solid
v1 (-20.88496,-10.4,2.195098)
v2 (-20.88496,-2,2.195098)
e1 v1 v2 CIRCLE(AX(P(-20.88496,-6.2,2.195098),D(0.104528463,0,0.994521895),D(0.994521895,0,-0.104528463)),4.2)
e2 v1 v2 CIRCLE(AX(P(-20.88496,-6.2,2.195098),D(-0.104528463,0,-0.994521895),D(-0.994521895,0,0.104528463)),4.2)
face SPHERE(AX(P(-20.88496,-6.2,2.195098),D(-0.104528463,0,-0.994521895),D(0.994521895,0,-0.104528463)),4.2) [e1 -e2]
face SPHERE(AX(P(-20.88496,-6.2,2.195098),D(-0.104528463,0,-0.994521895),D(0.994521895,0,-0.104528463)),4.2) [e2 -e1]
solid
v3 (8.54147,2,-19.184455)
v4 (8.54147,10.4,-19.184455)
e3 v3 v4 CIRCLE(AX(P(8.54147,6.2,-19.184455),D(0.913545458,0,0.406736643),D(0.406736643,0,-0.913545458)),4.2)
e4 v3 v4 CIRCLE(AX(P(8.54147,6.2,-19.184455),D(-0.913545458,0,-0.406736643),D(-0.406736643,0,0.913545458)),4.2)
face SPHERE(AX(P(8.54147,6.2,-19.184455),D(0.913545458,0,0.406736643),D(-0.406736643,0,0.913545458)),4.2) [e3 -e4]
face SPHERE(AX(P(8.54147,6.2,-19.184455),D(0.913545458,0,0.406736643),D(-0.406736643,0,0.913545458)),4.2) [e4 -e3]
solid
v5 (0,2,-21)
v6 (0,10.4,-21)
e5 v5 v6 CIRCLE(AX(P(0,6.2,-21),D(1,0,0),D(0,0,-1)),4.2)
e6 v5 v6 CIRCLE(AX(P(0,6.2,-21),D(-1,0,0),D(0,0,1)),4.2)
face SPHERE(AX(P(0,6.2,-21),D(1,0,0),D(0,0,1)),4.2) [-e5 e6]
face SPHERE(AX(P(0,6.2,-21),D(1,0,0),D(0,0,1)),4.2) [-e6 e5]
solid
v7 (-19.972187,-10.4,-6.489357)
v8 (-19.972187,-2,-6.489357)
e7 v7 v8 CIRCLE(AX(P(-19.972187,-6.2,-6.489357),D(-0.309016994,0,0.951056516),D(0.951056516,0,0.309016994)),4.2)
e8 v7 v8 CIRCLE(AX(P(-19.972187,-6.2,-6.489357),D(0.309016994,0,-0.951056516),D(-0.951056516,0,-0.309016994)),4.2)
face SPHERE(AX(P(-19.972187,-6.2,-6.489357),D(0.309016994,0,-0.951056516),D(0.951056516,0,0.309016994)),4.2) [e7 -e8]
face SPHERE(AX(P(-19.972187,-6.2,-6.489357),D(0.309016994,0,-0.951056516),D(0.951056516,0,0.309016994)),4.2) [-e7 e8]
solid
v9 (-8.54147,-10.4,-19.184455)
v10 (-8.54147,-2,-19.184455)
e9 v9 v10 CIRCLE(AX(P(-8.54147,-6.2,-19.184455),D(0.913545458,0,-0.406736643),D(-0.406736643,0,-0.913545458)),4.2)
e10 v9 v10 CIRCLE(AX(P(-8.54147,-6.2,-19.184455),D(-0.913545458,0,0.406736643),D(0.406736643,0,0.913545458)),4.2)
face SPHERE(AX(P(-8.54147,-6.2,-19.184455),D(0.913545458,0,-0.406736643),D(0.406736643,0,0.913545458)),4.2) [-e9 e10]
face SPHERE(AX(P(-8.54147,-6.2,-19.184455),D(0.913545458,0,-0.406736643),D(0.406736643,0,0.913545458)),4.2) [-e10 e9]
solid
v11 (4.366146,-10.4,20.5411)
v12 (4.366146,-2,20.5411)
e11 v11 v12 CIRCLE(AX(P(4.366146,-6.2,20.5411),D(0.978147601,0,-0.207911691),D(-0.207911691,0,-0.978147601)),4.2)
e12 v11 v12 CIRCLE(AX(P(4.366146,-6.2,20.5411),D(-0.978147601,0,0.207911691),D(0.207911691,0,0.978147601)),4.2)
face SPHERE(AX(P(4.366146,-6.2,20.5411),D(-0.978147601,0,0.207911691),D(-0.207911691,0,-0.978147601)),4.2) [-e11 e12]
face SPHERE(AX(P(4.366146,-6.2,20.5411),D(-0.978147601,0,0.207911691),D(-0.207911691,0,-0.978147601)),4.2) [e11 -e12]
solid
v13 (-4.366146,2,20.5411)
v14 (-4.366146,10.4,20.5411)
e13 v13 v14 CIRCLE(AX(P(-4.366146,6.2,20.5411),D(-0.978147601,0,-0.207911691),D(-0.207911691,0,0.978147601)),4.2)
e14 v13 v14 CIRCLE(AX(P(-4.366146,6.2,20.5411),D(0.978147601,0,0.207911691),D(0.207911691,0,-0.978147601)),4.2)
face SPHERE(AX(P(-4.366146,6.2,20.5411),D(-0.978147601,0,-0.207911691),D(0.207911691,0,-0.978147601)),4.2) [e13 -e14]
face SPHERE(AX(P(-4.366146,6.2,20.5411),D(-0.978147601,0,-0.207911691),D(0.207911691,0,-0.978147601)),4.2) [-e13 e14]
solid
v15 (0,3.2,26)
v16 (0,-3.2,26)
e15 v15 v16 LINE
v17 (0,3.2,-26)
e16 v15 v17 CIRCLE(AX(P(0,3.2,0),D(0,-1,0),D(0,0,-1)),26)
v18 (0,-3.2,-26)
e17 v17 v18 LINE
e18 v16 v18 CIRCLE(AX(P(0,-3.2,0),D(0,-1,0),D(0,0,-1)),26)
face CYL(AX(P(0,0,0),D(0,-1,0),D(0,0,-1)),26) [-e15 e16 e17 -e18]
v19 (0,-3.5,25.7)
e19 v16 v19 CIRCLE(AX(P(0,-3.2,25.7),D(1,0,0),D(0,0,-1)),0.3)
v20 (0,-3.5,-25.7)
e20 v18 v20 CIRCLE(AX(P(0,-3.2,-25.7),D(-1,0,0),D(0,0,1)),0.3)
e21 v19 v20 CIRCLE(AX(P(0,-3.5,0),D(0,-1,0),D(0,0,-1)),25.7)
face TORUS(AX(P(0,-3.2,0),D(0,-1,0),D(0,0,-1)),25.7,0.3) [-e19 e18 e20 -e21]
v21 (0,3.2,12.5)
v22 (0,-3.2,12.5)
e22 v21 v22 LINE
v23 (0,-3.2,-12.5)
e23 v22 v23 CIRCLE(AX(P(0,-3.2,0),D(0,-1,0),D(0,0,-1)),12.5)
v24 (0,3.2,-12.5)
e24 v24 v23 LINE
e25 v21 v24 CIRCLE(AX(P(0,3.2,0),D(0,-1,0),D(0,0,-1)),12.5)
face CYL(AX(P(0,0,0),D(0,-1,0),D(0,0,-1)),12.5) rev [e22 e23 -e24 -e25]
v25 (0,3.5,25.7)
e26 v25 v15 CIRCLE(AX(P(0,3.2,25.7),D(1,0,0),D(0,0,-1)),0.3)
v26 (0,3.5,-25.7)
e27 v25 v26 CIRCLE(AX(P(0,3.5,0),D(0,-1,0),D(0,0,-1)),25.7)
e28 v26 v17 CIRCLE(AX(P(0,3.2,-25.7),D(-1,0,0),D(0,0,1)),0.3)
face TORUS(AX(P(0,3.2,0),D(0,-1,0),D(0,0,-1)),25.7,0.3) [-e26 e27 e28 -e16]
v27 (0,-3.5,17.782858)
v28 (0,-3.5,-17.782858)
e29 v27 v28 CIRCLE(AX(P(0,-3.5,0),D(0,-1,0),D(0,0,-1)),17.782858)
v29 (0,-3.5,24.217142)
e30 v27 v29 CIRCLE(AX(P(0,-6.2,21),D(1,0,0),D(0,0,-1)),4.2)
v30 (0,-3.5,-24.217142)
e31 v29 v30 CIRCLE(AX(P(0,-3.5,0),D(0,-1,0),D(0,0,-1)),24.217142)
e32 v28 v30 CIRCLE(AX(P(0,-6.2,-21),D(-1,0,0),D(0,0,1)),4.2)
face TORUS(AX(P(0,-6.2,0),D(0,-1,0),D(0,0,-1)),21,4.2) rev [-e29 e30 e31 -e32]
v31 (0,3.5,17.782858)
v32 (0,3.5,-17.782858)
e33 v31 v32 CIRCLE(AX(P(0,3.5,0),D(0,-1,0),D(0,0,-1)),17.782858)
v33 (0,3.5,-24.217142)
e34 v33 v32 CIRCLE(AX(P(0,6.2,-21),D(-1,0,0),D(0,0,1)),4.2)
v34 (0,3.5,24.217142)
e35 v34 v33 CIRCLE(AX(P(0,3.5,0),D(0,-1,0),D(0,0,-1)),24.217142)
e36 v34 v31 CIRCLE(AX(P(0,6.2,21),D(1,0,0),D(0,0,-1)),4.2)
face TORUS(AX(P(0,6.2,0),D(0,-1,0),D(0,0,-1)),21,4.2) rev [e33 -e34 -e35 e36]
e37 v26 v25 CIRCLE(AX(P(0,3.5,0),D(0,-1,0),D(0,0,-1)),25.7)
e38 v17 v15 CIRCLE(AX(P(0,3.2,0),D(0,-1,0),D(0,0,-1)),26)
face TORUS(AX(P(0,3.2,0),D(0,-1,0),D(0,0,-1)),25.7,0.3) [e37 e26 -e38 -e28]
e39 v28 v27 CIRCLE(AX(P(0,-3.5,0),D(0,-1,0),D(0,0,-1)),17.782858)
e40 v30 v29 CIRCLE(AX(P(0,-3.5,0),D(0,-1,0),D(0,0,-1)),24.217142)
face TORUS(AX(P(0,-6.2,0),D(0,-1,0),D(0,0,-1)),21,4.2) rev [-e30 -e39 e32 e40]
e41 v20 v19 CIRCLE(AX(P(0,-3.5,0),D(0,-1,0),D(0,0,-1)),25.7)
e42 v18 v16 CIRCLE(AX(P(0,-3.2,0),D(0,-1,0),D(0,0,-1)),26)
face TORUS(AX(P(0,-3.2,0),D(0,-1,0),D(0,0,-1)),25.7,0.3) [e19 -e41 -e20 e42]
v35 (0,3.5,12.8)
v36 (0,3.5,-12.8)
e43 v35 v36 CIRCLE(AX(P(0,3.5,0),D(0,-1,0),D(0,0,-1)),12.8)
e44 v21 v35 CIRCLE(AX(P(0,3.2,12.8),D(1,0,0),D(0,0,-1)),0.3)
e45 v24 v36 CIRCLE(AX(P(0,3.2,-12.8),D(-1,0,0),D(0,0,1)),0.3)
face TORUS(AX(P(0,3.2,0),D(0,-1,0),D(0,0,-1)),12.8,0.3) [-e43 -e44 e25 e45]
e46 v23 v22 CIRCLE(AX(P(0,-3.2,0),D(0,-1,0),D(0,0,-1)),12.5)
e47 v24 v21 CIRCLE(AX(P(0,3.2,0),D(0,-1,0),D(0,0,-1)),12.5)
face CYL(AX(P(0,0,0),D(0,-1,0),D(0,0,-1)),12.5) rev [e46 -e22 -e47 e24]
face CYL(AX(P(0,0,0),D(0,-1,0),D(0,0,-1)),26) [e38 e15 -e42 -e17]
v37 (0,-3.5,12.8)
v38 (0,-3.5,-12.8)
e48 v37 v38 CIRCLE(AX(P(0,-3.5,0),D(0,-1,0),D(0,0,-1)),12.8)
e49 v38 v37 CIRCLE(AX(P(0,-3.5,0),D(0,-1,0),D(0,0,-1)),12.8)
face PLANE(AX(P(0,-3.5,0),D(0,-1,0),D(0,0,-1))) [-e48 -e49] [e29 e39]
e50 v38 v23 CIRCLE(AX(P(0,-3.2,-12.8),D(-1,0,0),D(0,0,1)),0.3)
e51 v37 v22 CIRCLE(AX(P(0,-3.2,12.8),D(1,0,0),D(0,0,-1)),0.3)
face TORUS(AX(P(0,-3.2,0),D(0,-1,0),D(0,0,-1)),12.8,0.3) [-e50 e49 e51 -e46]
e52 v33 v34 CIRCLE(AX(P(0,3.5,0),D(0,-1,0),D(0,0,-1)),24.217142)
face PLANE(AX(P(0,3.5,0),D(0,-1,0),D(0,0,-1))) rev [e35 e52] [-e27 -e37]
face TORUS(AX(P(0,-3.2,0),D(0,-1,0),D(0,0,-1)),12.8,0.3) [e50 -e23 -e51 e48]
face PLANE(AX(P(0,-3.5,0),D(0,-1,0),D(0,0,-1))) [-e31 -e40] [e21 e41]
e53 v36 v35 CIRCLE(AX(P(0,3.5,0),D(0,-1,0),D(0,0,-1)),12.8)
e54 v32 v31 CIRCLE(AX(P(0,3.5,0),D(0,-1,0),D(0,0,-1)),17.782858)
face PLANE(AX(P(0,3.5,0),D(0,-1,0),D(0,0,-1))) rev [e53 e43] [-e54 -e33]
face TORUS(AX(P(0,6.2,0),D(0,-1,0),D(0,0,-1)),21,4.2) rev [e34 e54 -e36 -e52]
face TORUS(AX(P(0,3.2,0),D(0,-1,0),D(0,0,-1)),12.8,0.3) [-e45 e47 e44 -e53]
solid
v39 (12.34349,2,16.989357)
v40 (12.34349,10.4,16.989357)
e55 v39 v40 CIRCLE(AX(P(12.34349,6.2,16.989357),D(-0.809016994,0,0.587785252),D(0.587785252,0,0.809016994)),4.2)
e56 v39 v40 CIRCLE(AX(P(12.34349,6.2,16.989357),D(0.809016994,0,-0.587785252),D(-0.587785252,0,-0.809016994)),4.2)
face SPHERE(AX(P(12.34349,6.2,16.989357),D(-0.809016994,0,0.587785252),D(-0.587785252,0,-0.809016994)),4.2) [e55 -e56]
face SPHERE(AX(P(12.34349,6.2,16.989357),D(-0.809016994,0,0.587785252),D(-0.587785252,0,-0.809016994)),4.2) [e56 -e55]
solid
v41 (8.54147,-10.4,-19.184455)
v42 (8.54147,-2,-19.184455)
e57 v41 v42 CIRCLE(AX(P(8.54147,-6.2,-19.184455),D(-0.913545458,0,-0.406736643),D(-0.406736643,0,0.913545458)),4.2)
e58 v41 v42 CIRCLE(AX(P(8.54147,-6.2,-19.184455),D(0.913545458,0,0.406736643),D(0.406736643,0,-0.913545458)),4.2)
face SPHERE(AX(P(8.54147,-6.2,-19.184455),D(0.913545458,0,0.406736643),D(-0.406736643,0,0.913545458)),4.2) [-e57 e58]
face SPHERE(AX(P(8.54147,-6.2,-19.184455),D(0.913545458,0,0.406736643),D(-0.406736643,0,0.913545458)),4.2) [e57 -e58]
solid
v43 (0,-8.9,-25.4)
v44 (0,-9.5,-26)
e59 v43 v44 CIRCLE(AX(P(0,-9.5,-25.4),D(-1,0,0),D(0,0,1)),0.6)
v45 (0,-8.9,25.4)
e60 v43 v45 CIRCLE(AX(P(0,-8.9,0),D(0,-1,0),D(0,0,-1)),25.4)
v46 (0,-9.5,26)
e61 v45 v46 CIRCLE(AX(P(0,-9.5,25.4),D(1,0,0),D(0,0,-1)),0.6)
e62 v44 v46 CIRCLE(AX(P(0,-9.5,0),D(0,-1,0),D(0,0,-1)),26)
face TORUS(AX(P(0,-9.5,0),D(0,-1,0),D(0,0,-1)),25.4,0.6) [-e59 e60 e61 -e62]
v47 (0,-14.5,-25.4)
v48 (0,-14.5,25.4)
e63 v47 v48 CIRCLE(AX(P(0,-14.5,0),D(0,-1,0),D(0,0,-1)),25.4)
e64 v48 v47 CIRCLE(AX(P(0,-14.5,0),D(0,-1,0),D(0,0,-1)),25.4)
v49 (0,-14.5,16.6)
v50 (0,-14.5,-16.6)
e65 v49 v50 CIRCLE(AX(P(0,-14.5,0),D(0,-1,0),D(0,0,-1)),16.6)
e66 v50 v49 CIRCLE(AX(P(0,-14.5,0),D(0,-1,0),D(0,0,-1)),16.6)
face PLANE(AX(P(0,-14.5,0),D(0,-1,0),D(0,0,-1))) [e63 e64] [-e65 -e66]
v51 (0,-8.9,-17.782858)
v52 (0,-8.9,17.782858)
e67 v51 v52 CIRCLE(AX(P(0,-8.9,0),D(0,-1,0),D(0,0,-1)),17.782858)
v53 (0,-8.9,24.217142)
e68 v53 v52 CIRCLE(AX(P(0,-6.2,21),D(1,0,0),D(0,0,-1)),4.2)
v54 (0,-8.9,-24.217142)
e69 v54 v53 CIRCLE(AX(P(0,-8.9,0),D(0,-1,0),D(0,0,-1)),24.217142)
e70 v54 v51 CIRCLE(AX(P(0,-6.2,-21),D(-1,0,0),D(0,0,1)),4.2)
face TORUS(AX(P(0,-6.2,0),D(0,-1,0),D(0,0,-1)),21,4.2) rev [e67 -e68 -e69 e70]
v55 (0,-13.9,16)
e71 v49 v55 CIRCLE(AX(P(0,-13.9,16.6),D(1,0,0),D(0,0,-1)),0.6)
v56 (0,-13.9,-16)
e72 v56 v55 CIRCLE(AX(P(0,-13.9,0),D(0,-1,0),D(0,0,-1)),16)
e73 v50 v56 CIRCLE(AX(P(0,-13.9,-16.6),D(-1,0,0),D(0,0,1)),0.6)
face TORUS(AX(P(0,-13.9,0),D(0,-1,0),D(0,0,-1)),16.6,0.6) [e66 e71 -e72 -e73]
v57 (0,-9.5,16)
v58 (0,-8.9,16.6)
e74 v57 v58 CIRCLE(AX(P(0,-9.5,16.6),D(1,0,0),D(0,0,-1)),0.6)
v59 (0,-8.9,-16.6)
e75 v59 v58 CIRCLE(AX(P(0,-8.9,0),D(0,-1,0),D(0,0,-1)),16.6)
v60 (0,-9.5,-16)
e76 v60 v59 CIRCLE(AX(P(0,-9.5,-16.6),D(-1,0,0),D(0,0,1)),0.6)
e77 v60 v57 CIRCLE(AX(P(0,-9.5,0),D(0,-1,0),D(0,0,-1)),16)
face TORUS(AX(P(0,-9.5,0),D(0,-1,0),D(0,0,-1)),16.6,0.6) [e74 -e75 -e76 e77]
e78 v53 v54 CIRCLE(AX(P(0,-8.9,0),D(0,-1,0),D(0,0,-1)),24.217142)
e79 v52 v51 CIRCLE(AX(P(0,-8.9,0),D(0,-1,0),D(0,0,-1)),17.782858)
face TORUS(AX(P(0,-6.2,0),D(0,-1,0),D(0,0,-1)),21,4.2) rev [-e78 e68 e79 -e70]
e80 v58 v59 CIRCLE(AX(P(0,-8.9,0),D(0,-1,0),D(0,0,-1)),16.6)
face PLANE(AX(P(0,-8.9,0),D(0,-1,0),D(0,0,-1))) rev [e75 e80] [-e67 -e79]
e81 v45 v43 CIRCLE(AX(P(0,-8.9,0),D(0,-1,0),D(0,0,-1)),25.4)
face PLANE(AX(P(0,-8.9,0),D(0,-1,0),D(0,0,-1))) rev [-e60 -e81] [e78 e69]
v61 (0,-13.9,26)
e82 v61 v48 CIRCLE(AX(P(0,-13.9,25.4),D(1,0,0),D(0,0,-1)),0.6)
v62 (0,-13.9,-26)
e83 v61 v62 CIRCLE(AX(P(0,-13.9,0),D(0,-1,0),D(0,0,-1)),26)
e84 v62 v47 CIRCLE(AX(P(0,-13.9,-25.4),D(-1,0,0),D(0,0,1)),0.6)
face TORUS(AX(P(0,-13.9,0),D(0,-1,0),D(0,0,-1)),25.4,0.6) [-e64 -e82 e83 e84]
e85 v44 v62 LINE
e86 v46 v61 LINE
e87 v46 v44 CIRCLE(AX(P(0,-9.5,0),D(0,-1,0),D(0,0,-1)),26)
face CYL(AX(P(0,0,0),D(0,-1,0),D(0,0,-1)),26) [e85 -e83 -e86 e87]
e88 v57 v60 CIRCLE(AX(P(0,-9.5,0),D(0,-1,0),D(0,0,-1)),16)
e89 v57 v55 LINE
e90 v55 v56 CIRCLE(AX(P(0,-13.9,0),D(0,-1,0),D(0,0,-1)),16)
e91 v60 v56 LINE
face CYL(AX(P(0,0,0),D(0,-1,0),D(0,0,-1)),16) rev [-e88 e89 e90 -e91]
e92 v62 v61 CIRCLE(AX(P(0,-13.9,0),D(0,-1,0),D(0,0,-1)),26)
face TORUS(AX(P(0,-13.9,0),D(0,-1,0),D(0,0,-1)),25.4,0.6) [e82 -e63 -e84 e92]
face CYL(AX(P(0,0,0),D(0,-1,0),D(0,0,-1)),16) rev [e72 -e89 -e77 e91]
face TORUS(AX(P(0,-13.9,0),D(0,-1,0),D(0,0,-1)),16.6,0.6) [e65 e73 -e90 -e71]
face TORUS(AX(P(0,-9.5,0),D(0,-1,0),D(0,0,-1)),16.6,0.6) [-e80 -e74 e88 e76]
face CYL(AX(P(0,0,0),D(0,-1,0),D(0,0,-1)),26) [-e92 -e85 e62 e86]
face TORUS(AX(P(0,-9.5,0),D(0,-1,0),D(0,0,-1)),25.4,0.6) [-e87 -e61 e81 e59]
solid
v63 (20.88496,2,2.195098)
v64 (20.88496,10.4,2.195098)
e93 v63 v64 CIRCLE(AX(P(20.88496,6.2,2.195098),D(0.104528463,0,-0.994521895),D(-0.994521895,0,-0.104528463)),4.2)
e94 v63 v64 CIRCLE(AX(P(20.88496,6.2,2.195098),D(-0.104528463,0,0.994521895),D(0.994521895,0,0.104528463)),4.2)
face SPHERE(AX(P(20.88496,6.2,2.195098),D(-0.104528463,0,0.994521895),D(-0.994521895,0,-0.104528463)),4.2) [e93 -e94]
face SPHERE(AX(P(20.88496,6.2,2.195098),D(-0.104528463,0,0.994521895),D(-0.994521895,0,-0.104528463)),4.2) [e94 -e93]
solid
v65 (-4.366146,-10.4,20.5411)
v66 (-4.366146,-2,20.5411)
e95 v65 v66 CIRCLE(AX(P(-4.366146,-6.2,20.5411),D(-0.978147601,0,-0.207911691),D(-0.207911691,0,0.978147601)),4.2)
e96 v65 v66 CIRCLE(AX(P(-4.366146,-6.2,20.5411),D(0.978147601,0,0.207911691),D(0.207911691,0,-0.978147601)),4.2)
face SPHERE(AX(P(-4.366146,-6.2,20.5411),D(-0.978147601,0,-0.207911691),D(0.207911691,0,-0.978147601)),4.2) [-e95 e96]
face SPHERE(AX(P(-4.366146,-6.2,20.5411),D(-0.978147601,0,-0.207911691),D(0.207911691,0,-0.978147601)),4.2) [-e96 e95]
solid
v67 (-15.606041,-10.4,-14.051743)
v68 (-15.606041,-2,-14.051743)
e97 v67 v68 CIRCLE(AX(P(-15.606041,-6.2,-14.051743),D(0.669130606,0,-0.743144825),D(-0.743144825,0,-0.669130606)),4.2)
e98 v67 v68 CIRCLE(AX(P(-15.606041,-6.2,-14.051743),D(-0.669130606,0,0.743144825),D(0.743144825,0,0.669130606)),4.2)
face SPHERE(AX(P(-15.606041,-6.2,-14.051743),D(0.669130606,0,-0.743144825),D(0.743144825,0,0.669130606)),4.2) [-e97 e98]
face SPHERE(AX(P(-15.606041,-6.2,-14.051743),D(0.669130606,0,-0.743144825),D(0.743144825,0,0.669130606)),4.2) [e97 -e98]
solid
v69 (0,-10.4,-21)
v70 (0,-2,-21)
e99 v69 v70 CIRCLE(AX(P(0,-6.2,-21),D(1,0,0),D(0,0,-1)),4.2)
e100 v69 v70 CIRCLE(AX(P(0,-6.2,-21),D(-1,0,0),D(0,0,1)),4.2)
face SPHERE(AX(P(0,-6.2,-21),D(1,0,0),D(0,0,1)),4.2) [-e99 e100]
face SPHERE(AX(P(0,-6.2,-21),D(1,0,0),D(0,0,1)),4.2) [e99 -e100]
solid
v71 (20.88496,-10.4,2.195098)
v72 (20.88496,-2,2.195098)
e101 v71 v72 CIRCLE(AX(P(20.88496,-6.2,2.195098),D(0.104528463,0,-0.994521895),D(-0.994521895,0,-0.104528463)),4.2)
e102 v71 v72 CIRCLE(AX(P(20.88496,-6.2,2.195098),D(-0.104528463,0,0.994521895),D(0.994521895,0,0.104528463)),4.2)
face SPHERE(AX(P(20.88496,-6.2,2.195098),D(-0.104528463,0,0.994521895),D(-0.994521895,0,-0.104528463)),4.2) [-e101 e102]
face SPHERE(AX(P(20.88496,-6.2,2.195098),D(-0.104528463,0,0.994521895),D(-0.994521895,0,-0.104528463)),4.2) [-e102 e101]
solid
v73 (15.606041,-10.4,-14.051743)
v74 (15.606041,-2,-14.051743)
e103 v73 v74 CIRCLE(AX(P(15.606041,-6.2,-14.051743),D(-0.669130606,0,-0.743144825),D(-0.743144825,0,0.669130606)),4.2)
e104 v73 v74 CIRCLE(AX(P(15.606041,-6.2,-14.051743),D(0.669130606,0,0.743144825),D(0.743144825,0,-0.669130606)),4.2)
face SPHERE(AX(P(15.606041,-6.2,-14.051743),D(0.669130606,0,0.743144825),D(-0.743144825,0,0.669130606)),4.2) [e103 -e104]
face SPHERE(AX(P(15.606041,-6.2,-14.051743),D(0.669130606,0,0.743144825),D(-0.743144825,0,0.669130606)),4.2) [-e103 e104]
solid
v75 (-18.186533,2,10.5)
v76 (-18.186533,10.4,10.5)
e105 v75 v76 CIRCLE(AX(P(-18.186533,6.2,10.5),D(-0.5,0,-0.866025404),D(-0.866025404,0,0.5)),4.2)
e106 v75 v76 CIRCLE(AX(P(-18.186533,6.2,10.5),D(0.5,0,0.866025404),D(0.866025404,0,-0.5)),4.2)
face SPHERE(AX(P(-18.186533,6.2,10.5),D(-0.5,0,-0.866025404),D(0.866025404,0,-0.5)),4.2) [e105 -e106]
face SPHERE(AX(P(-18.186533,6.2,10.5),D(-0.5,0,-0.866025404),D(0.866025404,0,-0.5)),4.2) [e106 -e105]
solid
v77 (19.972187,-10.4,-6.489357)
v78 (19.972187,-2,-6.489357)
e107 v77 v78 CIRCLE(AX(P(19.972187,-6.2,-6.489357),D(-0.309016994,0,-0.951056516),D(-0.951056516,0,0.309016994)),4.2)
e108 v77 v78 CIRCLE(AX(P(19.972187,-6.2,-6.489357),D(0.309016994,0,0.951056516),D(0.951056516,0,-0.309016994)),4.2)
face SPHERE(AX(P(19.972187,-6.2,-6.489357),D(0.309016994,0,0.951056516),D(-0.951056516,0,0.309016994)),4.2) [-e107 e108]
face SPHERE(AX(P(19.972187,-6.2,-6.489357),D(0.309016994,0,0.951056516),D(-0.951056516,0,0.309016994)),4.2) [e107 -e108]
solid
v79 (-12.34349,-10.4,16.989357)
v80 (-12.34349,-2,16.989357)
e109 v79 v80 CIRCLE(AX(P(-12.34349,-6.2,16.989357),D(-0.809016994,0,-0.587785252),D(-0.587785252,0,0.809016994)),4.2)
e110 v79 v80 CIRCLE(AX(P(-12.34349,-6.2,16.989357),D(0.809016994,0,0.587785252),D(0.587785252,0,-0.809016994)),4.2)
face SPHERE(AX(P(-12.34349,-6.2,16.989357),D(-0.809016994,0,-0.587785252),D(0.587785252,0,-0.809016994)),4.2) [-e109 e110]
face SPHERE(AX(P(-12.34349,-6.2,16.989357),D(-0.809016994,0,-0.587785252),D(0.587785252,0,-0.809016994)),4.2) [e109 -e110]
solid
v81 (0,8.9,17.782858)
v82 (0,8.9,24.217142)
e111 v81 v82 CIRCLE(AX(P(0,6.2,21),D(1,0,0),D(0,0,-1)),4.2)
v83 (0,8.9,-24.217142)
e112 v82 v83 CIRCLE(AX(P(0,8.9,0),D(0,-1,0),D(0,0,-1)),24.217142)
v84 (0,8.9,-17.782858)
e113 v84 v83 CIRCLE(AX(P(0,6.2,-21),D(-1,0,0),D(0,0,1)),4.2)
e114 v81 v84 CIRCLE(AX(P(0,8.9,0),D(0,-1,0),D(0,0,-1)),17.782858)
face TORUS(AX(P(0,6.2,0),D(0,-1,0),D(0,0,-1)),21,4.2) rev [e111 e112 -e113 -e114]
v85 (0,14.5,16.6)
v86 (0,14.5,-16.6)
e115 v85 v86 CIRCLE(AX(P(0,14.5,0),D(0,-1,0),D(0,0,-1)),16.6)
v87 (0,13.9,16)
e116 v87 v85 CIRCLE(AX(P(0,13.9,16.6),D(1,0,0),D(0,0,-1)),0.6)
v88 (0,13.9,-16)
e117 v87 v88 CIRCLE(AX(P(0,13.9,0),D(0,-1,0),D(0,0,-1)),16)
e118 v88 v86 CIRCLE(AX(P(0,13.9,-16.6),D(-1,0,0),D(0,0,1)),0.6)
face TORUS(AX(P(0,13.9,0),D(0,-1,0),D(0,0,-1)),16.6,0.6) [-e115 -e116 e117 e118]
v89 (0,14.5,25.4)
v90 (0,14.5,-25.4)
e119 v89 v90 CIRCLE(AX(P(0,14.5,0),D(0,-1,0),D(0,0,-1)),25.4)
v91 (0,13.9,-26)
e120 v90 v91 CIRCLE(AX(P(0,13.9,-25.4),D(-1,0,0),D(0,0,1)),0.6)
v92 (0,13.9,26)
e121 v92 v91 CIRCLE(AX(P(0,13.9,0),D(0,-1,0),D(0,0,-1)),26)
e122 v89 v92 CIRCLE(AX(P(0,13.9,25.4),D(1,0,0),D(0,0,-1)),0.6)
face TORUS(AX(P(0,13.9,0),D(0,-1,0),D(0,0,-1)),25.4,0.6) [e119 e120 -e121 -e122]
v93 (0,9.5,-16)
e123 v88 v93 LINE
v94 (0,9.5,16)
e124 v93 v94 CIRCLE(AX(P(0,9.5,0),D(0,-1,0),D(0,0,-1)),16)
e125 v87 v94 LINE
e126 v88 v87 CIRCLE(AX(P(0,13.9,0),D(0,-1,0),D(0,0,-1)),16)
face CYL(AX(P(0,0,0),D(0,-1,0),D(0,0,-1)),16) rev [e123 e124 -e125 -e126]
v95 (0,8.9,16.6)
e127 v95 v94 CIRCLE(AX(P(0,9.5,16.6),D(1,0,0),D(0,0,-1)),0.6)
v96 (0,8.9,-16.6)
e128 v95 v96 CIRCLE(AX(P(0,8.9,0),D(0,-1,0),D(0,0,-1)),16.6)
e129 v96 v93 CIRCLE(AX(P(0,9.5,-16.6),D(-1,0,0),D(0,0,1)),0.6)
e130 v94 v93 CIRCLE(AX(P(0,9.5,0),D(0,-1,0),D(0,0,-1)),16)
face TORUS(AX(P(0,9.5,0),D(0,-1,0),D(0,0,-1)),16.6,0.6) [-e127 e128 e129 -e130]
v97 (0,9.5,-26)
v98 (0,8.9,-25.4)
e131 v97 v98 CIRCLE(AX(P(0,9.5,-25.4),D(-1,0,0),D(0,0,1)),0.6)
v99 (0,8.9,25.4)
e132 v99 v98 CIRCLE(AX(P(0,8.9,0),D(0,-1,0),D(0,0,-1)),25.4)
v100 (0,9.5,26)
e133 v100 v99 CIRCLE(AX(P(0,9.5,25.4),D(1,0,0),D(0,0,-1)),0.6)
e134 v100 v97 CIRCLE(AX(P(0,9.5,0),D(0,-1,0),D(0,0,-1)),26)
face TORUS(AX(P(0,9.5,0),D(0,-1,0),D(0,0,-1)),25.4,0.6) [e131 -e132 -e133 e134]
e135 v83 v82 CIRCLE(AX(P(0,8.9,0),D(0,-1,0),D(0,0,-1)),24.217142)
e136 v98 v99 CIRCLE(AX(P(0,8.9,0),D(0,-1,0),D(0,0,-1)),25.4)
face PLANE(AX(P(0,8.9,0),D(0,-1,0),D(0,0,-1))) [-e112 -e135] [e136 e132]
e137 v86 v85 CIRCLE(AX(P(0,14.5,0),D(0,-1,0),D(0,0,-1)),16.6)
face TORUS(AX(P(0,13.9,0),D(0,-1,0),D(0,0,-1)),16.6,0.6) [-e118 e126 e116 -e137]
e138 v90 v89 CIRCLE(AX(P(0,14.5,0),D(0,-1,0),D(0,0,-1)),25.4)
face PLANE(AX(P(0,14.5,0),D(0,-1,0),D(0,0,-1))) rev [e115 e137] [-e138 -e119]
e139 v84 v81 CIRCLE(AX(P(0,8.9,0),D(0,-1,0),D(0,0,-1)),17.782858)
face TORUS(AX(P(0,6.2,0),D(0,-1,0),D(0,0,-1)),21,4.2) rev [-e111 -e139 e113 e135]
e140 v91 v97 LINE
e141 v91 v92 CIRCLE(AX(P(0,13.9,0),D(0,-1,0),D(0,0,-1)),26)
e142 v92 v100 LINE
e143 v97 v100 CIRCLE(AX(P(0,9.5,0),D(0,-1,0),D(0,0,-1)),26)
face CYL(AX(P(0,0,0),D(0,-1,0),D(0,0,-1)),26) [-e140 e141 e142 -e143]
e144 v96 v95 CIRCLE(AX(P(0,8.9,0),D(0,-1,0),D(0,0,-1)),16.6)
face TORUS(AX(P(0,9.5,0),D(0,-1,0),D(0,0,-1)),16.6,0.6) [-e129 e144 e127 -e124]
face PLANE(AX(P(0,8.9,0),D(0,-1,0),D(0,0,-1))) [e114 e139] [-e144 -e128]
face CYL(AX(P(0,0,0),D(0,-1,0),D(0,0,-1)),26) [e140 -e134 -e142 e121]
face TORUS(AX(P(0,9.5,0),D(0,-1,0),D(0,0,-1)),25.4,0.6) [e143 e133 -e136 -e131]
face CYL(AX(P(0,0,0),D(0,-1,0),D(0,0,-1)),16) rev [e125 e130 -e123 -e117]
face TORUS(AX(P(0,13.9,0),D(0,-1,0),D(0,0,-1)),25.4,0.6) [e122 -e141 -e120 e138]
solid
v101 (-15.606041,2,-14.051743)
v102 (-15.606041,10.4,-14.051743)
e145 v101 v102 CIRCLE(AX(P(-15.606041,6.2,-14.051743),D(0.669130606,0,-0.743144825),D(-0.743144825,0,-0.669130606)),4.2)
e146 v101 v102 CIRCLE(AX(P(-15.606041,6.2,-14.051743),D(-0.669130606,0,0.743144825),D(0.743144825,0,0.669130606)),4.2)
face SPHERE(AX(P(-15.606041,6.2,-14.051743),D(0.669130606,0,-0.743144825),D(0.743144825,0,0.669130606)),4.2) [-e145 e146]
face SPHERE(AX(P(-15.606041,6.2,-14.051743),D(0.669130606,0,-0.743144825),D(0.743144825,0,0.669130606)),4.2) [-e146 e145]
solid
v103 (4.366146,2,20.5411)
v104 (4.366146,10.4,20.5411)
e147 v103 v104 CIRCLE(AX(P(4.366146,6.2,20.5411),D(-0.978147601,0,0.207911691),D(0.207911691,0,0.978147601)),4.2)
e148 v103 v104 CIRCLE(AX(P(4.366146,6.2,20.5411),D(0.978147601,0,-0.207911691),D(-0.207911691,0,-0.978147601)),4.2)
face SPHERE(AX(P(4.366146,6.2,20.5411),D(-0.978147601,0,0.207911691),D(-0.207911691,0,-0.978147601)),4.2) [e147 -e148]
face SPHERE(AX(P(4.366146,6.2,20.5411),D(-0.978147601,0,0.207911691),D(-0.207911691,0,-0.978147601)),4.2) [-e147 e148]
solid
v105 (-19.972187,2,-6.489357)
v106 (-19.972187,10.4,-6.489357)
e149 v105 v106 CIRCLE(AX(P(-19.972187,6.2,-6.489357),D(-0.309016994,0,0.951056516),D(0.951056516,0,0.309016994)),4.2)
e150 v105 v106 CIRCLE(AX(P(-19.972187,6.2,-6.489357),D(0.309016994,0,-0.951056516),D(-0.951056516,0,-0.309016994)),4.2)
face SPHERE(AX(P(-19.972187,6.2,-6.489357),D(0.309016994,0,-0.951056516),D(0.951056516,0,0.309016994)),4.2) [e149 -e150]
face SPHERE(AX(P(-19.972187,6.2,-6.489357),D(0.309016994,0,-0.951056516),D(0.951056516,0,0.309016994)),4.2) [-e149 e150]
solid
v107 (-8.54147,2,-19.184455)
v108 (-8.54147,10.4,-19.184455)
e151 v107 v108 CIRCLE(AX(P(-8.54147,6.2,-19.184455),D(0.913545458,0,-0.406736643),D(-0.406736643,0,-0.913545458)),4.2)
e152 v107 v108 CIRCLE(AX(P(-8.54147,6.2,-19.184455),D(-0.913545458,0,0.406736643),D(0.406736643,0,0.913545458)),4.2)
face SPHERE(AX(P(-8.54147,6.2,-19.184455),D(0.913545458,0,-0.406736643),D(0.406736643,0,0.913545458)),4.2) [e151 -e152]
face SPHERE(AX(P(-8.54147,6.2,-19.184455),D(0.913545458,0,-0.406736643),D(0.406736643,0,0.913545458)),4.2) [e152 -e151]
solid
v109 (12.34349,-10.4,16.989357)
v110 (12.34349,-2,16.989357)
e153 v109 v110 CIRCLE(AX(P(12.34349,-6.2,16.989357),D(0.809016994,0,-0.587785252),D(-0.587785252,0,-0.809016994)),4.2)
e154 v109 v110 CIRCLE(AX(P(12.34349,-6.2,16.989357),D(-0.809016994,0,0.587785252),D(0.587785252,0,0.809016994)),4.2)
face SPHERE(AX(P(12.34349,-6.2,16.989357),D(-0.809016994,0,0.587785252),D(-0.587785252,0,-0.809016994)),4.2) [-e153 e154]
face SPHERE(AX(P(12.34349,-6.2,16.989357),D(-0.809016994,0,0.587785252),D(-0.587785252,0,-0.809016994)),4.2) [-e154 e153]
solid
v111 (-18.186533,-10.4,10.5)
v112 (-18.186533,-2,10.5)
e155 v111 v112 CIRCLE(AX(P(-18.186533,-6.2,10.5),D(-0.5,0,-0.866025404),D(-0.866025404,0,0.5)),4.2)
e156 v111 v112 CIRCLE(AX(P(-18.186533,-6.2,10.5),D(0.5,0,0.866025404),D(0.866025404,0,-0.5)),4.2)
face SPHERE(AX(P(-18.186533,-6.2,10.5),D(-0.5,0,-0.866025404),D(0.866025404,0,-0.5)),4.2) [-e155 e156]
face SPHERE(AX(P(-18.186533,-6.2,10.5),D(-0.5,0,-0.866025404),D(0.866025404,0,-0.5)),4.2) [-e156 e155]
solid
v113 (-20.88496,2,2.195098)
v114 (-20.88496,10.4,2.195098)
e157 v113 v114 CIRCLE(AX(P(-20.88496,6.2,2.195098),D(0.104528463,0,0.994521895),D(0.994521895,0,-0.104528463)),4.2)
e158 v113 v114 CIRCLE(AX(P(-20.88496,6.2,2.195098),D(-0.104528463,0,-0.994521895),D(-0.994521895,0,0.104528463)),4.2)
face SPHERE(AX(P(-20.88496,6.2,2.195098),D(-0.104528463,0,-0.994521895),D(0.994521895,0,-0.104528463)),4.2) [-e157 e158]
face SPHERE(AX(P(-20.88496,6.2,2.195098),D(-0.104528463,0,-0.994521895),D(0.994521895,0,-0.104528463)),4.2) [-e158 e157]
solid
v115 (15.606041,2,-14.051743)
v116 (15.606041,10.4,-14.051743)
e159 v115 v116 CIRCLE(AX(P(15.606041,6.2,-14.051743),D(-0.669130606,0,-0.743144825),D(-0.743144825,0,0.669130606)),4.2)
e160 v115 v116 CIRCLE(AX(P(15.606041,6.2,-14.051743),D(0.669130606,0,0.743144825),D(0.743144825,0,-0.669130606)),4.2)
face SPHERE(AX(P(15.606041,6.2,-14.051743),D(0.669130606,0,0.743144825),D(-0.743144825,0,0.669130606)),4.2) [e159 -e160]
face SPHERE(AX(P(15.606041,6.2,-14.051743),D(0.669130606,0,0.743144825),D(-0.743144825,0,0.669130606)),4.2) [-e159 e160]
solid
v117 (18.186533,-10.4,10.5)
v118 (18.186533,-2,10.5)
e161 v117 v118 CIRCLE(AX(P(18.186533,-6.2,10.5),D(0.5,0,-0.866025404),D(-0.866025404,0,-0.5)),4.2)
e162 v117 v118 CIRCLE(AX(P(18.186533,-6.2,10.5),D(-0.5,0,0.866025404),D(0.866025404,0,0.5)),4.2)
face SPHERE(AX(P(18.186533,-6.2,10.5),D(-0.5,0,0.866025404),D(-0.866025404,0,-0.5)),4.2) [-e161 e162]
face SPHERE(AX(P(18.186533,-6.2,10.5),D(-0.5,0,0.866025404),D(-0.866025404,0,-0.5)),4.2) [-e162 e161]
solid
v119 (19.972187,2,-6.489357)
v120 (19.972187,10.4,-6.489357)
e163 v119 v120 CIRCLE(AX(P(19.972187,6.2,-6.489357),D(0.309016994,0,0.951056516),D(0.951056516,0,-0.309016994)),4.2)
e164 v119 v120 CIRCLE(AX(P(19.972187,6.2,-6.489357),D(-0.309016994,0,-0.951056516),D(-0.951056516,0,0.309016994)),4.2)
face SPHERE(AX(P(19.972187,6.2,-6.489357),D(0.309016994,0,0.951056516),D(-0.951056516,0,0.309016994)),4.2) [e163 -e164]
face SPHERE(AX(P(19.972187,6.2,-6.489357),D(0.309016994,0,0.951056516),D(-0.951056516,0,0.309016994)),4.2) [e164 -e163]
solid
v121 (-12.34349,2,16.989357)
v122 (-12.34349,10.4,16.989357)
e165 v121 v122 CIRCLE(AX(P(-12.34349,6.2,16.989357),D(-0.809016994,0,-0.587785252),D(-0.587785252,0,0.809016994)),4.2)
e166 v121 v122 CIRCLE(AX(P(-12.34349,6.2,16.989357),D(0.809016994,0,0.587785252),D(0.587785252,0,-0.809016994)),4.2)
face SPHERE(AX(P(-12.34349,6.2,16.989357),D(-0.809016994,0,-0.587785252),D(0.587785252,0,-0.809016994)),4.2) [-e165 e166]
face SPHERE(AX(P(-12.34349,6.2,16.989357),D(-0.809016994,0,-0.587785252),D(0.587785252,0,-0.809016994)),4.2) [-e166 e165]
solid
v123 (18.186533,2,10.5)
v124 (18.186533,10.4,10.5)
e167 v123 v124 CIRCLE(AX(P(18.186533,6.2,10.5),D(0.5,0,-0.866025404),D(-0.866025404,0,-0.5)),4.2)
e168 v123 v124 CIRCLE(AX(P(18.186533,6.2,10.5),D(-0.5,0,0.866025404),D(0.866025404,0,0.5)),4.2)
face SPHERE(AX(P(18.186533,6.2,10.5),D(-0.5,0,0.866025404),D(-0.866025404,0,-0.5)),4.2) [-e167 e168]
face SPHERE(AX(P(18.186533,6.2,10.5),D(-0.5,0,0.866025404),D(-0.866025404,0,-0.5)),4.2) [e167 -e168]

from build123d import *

# Parameters (mm, degrees)
CIRPATTERN5_COUNT = 15


with BuildPart() as part:
    # Sketch2 → Revolve1 (revolve)
    with BuildSketch(Plane(origin=(0, 0, 0), x_dir=(0, 0, -1), z_dir=(1, 0, 0))):
        with BuildLine():
            ThreePointArc((24.217141588, 8.9), (21, 10.4), (17.782858412, 8.9))
            Line((17.782858412, 8.9), (16.6, 8.9))
            ThreePointArc((16.6, 8.9), (16.175735931, 9.075735931), (16, 9.5))
            Line((16, 9.5), (16, 13.9))
            ThreePointArc((16, 13.9), (16.175735931, 14.324264069), (16.6, 14.5))
            Line((16.6, 14.5), (25.4, 14.5))
            ThreePointArc((25.4, 14.5), (25.824264069, 14.324264069), (26, 13.9))
            Line((26, 13.9), (26, 9.5))
            ThreePointArc((26, 9.5), (25.824264069, 9.075735931), (25.4, 8.9))
            Line((25.4, 8.9), (24.217141588, 8.9))
        make_face()
        with BuildLine():
            ThreePointArc((17.782858412, 3.5), (21, 2), (24.217141588, 3.5))
            Line((24.217141588, 3.5), (25.7, 3.5))
            ThreePointArc((25.7, 3.5), (25.912132034, 3.412132034), (26, 3.2))
            Line((26, 3.2), (26, -3.2))
            ThreePointArc((26, -3.2), (25.912132034, -3.412132034), (25.7, -3.5))
            Line((25.7, -3.5), (24.217141588, -3.5))
            ThreePointArc((24.217141588, -3.5), (21, -2), (17.782858412, -3.5))
            Line((17.782858412, -3.5), (12.8, -3.5))
            ThreePointArc((12.8, -3.5), (12.587867966, -3.412132034), (12.5, -3.2))
            Line((12.5, -3.2), (12.5, 3.2))
            ThreePointArc((12.5, 3.2), (12.587867966, 3.412132034), (12.8, 3.5))
            Line((12.8, 3.5), (17.782858412, 3.5))
        make_face()
        with BuildLine():
            ThreePointArc((17.782858412, -8.9), (21, -10.4), (24.217141588, -8.9))
            Line((24.217141588, -8.9), (25.4, -8.9))
            ThreePointArc((25.4, -8.9), (25.824264069, -9.075735931), (26, -9.5))
            Line((26, -9.5), (26, -13.9))
            ThreePointArc((26, -13.9), (25.824264069, -14.324264069), (25.4, -14.5))
            Line((25.4, -14.5), (16.6, -14.5))
            ThreePointArc((16.6, -14.5), (16.175735931, -14.324264069), (16, -13.9))
            Line((16, -13.9), (16, -9.5))
            ThreePointArc((16, -9.5), (16.175735931, -9.075735931), (16.6, -8.9))
            Line((16.6, -8.9), (17.782858412, -8.9))
        make_face()
    revolve(axis=Axis((0, 0, 0), (0, 1, 0)))


with BuildPart() as body_2:
    # Sketch3 → Revolve2 (revolve)
    with BuildSketch(Plane(origin=(0, 0, 0), x_dir=(0, 0, -1), z_dir=(1, 0, 0))):
        with BuildLine():
            ThreePointArc((21, 2), (25.2, 6.2), (21, 10.4))
            Line((21, 10.4), (21, 2))
        make_face()
        with BuildLine():
            ThreePointArc((21, -10.4), (25.2, -6.2), (21, -2))
            Line((21, -2), (21, -10.4))
        make_face()
    revolve(axis=Axis((0, 10.4, -21), (0, -1, 0)))


with BuildPart() as cirpattern5_1:
    # CirPattern5: pattern copy
    add(body_2.part.rotate(Axis((0, 0, 0), (0, 1, 0)), 1 * 360 / CIRPATTERN5_COUNT))


with BuildPart() as cirpattern5_2:
    # CirPattern5: pattern copy
    add(body_2.part.rotate(Axis((0, 0, 0), (0, 1, 0)), 2 * 360 / CIRPATTERN5_COUNT))


with BuildPart() as cirpattern5_3:
    # CirPattern5: pattern copy
    add(body_2.part.rotate(Axis((0, 0, 0), (0, 1, 0)), 3 * 360 / CIRPATTERN5_COUNT))


with BuildPart() as cirpattern5_4:
    # CirPattern5: pattern copy
    add(body_2.part.rotate(Axis((0, 0, 0), (0, 1, 0)), 4 * 360 / CIRPATTERN5_COUNT))


with BuildPart() as cirpattern5_5:
    # CirPattern5: pattern copy
    add(body_2.part.rotate(Axis((0, 0, 0), (0, 1, 0)), 5 * 360 / CIRPATTERN5_COUNT))


with BuildPart() as cirpattern5_6:
    # CirPattern5: pattern copy
    add(body_2.part.rotate(Axis((0, 0, 0), (0, 1, 0)), 6 * 360 / CIRPATTERN5_COUNT))


with BuildPart() as cirpattern5_7:
    # CirPattern5: pattern copy
    add(body_2.part.rotate(Axis((0, 0, 0), (0, 1, 0)), 7 * 360 / CIRPATTERN5_COUNT))


with BuildPart() as cirpattern5_8:
    # CirPattern5: pattern copy
    add(body_2.part.rotate(Axis((0, 0, 0), (0, 1, 0)), 8 * 360 / CIRPATTERN5_COUNT))


with BuildPart() as cirpattern5_9:
    # CirPattern5: pattern copy
    add(body_2.part.rotate(Axis((0, 0, 0), (0, 1, 0)), 9 * 360 / CIRPATTERN5_COUNT))


with BuildPart() as cirpattern5_10:
    # CirPattern5: pattern copy
    add(body_2.part.rotate(Axis((0, 0, 0), (0, 1, 0)), 10 * 360 / CIRPATTERN5_COUNT))


with BuildPart() as cirpattern5_11:
    # CirPattern5: pattern copy
    add(body_2.part.rotate(Axis((0, 0, 0), (0, 1, 0)), 11 * 360 / CIRPATTERN5_COUNT))


with BuildPart() as cirpattern5_12:
    # CirPattern5: pattern copy
    add(body_2.part.rotate(Axis((0, 0, 0), (0, 1, 0)), 12 * 360 / CIRPATTERN5_COUNT))


with BuildPart() as cirpattern5_13:
    # CirPattern5: pattern copy
    add(body_2.part.rotate(Axis((0, 0, 0), (0, 1, 0)), 13 * 360 / CIRPATTERN5_COUNT))


with BuildPart() as cirpattern5_14:
    # CirPattern5: pattern copy
    add(body_2.part.rotate(Axis((0, 0, 0), (0, 1, 0)), 14 * 360 / CIRPATTERN5_COUNT))


solid = Compound([part.part, body_2.part, cirpattern5_1.part, cirpattern5_2.part, cirpattern5_3.part, cirpattern5_4.part, cirpattern5_5.part, cirpattern5_6.part, cirpattern5_7.part, cirpattern5_8.part, cirpattern5_9.part, cirpattern5_10.part, cirpattern5_11.part, cirpattern5_12.part, cirpattern5_13.part, cirpattern5_14.part])
